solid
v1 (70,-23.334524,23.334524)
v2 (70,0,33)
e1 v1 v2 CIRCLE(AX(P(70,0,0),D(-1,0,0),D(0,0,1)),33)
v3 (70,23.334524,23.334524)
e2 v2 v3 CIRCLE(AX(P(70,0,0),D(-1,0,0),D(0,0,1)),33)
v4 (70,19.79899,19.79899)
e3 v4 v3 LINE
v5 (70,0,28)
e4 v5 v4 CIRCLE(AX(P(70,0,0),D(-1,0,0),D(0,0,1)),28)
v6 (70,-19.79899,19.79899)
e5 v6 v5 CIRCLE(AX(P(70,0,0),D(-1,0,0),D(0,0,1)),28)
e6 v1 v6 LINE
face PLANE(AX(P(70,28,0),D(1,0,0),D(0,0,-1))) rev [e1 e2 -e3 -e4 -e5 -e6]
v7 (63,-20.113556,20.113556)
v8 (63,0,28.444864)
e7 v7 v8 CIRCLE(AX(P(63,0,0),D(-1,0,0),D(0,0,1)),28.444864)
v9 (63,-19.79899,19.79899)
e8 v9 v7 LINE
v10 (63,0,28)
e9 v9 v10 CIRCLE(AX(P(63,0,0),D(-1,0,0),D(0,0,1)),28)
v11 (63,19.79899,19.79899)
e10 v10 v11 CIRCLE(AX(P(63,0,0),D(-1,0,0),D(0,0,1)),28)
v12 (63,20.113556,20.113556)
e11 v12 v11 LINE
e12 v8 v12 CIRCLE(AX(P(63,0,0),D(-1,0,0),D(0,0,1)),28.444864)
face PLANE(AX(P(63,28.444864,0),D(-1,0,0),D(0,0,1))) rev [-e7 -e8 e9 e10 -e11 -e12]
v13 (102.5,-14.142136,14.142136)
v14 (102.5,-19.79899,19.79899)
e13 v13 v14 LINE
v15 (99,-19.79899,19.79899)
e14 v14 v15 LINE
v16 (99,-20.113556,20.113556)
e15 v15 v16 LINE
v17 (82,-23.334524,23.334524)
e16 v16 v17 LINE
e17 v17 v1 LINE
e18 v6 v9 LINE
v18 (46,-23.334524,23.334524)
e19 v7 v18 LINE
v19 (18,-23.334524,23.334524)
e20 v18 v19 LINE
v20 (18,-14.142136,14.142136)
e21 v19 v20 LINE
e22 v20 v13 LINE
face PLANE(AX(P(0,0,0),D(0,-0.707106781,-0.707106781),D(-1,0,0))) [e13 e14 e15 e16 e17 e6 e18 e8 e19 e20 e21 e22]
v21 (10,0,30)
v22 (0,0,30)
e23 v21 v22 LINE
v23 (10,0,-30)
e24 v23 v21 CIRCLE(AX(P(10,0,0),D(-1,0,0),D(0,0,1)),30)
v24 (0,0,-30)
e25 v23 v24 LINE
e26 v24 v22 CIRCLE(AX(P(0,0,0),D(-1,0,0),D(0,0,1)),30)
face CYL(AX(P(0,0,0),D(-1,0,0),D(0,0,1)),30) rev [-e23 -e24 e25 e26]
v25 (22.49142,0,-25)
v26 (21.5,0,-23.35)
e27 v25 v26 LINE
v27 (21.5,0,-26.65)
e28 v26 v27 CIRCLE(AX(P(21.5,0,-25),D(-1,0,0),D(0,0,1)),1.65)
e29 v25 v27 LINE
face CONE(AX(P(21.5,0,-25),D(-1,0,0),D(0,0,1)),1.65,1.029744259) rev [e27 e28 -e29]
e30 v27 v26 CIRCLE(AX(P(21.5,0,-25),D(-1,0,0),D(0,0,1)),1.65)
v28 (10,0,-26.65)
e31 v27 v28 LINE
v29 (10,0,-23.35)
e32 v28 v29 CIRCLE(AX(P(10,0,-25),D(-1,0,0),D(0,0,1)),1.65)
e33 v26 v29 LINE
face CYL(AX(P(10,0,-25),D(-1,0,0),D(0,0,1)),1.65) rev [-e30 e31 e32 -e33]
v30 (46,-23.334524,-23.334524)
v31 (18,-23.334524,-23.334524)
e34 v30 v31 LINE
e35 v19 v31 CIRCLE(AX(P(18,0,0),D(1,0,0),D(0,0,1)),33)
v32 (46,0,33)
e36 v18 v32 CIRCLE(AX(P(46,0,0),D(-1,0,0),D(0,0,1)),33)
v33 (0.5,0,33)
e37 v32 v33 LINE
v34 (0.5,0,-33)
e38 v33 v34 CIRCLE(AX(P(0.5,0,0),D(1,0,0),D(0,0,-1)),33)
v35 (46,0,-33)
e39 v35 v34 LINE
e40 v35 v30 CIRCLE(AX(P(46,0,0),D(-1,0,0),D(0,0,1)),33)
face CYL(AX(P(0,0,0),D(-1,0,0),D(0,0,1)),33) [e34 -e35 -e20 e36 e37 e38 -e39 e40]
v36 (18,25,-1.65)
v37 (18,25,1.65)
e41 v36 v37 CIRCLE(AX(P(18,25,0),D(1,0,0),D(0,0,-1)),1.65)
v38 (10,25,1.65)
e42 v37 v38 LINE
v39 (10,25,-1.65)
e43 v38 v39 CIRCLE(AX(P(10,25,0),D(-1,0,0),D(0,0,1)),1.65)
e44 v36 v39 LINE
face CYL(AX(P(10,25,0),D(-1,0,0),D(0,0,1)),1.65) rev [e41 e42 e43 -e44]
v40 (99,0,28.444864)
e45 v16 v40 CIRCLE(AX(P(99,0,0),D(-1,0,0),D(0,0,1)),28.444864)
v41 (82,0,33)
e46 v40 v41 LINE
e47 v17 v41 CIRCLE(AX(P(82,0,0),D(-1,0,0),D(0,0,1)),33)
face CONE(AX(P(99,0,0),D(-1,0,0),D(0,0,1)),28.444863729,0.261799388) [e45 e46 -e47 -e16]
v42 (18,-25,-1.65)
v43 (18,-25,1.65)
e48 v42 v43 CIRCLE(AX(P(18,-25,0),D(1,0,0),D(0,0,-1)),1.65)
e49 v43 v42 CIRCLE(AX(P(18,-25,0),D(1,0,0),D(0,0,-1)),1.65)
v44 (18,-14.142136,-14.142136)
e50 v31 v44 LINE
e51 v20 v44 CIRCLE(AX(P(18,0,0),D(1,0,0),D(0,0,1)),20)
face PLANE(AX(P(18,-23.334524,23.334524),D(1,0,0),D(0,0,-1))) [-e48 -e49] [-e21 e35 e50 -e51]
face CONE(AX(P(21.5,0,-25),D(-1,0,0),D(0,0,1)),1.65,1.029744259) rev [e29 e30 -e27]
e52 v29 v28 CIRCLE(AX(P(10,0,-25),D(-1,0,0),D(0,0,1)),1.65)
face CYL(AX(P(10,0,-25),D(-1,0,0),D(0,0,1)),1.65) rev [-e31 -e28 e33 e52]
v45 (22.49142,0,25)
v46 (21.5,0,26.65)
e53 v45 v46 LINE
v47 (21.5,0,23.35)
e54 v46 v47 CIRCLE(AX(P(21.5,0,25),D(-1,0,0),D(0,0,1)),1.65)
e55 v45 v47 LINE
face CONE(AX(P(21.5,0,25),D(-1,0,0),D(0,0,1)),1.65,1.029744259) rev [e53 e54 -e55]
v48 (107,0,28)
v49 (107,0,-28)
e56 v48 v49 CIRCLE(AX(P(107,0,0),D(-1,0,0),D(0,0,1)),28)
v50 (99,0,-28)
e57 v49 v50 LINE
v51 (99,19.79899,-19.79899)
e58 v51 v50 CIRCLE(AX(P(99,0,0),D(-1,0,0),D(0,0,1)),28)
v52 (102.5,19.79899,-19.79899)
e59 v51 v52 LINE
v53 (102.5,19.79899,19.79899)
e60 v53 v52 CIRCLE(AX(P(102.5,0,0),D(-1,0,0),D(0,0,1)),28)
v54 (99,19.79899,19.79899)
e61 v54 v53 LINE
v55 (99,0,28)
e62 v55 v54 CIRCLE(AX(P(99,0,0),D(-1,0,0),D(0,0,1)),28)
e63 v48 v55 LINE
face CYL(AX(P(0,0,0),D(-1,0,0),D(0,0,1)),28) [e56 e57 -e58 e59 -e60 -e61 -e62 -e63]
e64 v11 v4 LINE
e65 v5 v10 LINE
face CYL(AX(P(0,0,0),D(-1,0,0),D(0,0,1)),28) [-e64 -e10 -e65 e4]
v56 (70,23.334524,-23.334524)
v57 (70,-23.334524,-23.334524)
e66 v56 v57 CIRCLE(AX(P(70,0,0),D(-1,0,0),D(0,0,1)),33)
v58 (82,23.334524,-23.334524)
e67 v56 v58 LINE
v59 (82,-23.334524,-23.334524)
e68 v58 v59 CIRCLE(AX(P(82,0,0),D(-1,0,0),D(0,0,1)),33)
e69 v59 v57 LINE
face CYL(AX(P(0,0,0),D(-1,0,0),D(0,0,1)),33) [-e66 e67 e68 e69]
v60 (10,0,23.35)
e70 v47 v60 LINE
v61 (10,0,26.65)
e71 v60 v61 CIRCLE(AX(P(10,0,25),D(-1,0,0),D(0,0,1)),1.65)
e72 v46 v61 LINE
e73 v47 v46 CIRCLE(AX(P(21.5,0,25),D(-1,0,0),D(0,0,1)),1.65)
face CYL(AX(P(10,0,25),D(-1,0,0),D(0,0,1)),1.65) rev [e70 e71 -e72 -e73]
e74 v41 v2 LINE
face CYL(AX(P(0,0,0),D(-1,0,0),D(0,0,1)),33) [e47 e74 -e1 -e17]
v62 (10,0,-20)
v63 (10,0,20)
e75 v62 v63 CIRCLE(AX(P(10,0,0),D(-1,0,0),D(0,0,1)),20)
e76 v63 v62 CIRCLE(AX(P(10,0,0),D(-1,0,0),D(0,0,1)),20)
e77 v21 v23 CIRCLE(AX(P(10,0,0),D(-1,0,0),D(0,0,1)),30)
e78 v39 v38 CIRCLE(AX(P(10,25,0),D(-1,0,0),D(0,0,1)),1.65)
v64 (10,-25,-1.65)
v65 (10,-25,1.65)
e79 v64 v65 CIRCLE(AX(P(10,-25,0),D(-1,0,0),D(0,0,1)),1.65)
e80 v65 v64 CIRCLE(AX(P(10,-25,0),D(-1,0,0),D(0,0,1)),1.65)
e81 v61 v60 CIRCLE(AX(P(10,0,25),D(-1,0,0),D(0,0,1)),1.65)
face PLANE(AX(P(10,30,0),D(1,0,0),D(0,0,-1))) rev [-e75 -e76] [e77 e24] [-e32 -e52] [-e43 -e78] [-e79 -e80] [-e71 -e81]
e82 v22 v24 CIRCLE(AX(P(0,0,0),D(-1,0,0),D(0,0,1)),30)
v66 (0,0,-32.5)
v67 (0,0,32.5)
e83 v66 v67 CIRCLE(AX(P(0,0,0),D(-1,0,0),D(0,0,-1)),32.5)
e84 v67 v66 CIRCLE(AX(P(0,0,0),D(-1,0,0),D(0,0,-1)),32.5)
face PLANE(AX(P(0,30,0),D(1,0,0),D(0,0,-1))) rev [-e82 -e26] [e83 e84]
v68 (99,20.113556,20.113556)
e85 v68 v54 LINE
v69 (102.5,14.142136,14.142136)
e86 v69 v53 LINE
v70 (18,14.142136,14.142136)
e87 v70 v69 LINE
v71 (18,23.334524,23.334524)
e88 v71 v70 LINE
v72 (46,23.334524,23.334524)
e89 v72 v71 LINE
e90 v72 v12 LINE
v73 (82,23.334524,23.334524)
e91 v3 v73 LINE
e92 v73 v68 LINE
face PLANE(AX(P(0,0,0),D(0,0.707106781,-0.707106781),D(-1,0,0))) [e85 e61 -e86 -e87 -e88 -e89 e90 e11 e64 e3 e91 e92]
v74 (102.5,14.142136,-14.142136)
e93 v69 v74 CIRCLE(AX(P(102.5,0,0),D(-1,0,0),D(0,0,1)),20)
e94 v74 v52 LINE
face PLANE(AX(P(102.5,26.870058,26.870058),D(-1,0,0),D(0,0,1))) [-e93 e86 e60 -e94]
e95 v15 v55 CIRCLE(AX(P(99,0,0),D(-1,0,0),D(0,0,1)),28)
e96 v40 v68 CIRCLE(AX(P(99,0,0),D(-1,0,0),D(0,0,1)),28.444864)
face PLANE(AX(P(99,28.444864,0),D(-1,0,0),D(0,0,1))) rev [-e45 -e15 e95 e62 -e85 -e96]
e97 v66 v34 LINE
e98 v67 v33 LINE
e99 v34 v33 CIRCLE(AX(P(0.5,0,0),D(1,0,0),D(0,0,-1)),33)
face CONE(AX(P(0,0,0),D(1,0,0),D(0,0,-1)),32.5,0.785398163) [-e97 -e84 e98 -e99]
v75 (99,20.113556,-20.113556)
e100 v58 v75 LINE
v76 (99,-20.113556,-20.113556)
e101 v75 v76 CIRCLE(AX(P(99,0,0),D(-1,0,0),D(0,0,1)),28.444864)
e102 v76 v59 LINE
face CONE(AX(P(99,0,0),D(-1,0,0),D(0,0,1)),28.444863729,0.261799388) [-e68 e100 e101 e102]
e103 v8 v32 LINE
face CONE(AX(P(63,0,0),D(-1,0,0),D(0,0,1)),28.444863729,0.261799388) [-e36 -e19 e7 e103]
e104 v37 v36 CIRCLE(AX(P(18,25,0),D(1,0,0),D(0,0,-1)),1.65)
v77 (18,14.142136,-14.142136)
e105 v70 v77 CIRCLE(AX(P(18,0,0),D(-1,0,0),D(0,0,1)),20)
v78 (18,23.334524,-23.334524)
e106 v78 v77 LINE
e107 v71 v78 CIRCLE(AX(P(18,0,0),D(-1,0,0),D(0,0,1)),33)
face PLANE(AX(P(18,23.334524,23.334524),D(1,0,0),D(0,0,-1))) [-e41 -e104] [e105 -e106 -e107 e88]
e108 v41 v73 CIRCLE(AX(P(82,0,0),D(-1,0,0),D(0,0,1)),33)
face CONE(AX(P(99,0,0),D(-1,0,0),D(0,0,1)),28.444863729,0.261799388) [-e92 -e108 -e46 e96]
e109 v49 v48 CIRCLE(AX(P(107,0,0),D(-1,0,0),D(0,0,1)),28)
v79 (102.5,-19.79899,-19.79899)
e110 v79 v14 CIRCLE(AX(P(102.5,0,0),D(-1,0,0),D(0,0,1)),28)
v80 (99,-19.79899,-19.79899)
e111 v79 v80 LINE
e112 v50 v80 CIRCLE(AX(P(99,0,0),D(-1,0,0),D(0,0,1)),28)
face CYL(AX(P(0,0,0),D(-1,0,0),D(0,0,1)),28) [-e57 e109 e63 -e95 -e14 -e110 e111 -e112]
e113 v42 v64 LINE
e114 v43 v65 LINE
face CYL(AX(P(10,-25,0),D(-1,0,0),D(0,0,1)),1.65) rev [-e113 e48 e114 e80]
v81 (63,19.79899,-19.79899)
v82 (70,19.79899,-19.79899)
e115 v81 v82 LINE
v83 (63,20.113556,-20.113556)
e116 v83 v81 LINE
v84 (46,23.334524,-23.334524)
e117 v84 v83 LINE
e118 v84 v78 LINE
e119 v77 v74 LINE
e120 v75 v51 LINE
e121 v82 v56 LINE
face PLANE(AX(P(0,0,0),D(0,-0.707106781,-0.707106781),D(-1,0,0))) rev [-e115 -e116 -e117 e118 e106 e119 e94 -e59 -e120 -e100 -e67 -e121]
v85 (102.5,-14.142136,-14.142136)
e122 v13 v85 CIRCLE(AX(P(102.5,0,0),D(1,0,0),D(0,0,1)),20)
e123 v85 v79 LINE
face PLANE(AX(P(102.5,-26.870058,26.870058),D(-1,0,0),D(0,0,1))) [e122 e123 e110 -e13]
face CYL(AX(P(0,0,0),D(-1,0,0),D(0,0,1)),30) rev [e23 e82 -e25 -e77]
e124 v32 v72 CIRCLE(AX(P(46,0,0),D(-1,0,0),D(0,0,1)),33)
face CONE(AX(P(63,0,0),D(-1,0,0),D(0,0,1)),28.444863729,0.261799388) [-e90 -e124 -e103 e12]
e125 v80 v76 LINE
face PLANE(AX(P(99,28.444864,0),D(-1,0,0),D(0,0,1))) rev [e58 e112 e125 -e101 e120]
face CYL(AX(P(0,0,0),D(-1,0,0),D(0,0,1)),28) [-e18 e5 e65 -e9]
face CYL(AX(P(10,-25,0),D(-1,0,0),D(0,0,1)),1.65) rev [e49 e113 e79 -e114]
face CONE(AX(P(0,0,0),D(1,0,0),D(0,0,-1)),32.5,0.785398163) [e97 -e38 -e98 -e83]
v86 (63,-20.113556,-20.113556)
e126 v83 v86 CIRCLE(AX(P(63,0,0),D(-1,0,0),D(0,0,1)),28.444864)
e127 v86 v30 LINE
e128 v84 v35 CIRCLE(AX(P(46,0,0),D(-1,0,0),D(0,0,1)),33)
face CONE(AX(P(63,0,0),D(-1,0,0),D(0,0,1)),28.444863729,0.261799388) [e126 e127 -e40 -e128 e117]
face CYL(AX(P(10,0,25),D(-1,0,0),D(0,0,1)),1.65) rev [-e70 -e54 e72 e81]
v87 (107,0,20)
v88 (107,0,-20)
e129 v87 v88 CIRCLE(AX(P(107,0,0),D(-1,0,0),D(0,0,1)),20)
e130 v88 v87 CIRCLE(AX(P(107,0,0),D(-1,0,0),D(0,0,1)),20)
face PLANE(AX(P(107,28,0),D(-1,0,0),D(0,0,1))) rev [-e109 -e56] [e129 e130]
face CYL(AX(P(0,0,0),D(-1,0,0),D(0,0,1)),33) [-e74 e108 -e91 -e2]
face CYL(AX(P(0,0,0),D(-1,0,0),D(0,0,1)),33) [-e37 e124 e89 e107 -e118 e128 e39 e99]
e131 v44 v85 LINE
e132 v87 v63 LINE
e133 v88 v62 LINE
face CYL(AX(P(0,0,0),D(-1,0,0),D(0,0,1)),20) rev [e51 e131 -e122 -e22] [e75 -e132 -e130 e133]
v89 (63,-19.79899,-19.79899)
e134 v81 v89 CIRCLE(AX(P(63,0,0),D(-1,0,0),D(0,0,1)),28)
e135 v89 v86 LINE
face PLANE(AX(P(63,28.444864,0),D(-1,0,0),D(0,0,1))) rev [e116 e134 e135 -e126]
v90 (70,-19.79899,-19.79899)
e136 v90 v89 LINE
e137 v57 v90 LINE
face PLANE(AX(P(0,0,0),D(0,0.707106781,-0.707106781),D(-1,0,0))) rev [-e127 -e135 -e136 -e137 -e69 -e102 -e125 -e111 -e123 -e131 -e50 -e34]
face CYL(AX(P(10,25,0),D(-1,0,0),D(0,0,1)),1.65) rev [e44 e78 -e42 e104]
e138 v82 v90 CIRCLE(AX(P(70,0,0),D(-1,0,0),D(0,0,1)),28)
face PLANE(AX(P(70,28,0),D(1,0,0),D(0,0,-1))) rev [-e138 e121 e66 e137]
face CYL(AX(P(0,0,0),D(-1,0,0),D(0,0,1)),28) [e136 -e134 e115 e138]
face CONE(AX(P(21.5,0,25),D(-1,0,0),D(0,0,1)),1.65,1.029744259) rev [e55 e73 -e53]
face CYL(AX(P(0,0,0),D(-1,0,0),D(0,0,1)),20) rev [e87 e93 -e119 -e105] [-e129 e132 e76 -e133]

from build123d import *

# Parameters (mm, degrees)
CUT_REVOLVE_1_ANGLE    = 90
CHAMFER_1_SIZE         = 0.5
HOLE_WIZARD_M4_1_D     = 3.3
HOLE_WIZARD_M4_1_DEPTH = 11.5
HOLE_WIZARD_M4_1_TIP   = 0.991420021


with BuildPart() as part:
    # 草图1 → 旋转1 (revolve)
    with BuildSketch(Plane.XY, mode=Mode.PRIVATE) as revolve_1_sk:
        Polygon((0, 30), (10, 30), (10, 20), (107, 20), (107, 28), (99, 28), (99, 28.444863729), (82, 33), (70, 33), (70, 28), (63, 28), (63, 28.444863729), (46, 33), (0, 33), align=None)
    revolve(revolve_1_sk.sketch.rotate(Axis((0, 0, 0), (1, 0, 0)), 90), axis=Axis((0, 0, 0), (1, 0, 0)))

    # 草图2 → 切除-旋转1 (revolve, symmetric, cut)
    with BuildSketch(Plane.XY) as cut_revolve_1_sk:
        Polygon((18, 33), (52.5, 33), (52.5, 38), (102.5, 38), (102.5, 20), (18, 20), align=None)
    cut_revolve_1 = revolve(axis=Axis((0, 0, 0), (1, 0, 0)), revolution_arc=CUT_REVOLVE_1_ANGLE / 2, mode=Mode.SUBTRACT)
    cut_revolve_1 = cut_revolve_1 + revolve(cut_revolve_1_sk.sketch, axis=Axis((0, 0, 0), (-1, 0, 0)), revolution_arc=CUT_REVOLVE_1_ANGLE / 2, mode=Mode.SUBTRACT)

    # 镜向1: 切除-旋转1 across plane
    add(cut_revolve_1.mirror(Plane.ZX), mode=Mode.SUBTRACT)

    # 倒角1
    chamfer_1_edges = [part.edges().sort_by_distance(p)[0] for p in [
        (0, 0, -33),
    ]]
    chamfer(chamfer_1_edges, length=CHAMFER_1_SIZE)

    # M4 螺纹孔1
    with Locations(Plane.ZY.offset(-10)):
        with Locations((0, 25), (25, 0), (0, -25), (-25, 0)):
            Hole(HOLE_WIZARD_M4_1_D / 2, depth=HOLE_WIZARD_M4_1_DEPTH)
            with Locations((0, 0, -(HOLE_WIZARD_M4_1_DEPTH + HOLE_WIZARD_M4_1_TIP / 2))):  # 118° drill point
                Cone(0, HOLE_WIZARD_M4_1_D / 2, HOLE_WIZARD_M4_1_TIP, mode=Mode.SUBTRACT)


solid = part.part
